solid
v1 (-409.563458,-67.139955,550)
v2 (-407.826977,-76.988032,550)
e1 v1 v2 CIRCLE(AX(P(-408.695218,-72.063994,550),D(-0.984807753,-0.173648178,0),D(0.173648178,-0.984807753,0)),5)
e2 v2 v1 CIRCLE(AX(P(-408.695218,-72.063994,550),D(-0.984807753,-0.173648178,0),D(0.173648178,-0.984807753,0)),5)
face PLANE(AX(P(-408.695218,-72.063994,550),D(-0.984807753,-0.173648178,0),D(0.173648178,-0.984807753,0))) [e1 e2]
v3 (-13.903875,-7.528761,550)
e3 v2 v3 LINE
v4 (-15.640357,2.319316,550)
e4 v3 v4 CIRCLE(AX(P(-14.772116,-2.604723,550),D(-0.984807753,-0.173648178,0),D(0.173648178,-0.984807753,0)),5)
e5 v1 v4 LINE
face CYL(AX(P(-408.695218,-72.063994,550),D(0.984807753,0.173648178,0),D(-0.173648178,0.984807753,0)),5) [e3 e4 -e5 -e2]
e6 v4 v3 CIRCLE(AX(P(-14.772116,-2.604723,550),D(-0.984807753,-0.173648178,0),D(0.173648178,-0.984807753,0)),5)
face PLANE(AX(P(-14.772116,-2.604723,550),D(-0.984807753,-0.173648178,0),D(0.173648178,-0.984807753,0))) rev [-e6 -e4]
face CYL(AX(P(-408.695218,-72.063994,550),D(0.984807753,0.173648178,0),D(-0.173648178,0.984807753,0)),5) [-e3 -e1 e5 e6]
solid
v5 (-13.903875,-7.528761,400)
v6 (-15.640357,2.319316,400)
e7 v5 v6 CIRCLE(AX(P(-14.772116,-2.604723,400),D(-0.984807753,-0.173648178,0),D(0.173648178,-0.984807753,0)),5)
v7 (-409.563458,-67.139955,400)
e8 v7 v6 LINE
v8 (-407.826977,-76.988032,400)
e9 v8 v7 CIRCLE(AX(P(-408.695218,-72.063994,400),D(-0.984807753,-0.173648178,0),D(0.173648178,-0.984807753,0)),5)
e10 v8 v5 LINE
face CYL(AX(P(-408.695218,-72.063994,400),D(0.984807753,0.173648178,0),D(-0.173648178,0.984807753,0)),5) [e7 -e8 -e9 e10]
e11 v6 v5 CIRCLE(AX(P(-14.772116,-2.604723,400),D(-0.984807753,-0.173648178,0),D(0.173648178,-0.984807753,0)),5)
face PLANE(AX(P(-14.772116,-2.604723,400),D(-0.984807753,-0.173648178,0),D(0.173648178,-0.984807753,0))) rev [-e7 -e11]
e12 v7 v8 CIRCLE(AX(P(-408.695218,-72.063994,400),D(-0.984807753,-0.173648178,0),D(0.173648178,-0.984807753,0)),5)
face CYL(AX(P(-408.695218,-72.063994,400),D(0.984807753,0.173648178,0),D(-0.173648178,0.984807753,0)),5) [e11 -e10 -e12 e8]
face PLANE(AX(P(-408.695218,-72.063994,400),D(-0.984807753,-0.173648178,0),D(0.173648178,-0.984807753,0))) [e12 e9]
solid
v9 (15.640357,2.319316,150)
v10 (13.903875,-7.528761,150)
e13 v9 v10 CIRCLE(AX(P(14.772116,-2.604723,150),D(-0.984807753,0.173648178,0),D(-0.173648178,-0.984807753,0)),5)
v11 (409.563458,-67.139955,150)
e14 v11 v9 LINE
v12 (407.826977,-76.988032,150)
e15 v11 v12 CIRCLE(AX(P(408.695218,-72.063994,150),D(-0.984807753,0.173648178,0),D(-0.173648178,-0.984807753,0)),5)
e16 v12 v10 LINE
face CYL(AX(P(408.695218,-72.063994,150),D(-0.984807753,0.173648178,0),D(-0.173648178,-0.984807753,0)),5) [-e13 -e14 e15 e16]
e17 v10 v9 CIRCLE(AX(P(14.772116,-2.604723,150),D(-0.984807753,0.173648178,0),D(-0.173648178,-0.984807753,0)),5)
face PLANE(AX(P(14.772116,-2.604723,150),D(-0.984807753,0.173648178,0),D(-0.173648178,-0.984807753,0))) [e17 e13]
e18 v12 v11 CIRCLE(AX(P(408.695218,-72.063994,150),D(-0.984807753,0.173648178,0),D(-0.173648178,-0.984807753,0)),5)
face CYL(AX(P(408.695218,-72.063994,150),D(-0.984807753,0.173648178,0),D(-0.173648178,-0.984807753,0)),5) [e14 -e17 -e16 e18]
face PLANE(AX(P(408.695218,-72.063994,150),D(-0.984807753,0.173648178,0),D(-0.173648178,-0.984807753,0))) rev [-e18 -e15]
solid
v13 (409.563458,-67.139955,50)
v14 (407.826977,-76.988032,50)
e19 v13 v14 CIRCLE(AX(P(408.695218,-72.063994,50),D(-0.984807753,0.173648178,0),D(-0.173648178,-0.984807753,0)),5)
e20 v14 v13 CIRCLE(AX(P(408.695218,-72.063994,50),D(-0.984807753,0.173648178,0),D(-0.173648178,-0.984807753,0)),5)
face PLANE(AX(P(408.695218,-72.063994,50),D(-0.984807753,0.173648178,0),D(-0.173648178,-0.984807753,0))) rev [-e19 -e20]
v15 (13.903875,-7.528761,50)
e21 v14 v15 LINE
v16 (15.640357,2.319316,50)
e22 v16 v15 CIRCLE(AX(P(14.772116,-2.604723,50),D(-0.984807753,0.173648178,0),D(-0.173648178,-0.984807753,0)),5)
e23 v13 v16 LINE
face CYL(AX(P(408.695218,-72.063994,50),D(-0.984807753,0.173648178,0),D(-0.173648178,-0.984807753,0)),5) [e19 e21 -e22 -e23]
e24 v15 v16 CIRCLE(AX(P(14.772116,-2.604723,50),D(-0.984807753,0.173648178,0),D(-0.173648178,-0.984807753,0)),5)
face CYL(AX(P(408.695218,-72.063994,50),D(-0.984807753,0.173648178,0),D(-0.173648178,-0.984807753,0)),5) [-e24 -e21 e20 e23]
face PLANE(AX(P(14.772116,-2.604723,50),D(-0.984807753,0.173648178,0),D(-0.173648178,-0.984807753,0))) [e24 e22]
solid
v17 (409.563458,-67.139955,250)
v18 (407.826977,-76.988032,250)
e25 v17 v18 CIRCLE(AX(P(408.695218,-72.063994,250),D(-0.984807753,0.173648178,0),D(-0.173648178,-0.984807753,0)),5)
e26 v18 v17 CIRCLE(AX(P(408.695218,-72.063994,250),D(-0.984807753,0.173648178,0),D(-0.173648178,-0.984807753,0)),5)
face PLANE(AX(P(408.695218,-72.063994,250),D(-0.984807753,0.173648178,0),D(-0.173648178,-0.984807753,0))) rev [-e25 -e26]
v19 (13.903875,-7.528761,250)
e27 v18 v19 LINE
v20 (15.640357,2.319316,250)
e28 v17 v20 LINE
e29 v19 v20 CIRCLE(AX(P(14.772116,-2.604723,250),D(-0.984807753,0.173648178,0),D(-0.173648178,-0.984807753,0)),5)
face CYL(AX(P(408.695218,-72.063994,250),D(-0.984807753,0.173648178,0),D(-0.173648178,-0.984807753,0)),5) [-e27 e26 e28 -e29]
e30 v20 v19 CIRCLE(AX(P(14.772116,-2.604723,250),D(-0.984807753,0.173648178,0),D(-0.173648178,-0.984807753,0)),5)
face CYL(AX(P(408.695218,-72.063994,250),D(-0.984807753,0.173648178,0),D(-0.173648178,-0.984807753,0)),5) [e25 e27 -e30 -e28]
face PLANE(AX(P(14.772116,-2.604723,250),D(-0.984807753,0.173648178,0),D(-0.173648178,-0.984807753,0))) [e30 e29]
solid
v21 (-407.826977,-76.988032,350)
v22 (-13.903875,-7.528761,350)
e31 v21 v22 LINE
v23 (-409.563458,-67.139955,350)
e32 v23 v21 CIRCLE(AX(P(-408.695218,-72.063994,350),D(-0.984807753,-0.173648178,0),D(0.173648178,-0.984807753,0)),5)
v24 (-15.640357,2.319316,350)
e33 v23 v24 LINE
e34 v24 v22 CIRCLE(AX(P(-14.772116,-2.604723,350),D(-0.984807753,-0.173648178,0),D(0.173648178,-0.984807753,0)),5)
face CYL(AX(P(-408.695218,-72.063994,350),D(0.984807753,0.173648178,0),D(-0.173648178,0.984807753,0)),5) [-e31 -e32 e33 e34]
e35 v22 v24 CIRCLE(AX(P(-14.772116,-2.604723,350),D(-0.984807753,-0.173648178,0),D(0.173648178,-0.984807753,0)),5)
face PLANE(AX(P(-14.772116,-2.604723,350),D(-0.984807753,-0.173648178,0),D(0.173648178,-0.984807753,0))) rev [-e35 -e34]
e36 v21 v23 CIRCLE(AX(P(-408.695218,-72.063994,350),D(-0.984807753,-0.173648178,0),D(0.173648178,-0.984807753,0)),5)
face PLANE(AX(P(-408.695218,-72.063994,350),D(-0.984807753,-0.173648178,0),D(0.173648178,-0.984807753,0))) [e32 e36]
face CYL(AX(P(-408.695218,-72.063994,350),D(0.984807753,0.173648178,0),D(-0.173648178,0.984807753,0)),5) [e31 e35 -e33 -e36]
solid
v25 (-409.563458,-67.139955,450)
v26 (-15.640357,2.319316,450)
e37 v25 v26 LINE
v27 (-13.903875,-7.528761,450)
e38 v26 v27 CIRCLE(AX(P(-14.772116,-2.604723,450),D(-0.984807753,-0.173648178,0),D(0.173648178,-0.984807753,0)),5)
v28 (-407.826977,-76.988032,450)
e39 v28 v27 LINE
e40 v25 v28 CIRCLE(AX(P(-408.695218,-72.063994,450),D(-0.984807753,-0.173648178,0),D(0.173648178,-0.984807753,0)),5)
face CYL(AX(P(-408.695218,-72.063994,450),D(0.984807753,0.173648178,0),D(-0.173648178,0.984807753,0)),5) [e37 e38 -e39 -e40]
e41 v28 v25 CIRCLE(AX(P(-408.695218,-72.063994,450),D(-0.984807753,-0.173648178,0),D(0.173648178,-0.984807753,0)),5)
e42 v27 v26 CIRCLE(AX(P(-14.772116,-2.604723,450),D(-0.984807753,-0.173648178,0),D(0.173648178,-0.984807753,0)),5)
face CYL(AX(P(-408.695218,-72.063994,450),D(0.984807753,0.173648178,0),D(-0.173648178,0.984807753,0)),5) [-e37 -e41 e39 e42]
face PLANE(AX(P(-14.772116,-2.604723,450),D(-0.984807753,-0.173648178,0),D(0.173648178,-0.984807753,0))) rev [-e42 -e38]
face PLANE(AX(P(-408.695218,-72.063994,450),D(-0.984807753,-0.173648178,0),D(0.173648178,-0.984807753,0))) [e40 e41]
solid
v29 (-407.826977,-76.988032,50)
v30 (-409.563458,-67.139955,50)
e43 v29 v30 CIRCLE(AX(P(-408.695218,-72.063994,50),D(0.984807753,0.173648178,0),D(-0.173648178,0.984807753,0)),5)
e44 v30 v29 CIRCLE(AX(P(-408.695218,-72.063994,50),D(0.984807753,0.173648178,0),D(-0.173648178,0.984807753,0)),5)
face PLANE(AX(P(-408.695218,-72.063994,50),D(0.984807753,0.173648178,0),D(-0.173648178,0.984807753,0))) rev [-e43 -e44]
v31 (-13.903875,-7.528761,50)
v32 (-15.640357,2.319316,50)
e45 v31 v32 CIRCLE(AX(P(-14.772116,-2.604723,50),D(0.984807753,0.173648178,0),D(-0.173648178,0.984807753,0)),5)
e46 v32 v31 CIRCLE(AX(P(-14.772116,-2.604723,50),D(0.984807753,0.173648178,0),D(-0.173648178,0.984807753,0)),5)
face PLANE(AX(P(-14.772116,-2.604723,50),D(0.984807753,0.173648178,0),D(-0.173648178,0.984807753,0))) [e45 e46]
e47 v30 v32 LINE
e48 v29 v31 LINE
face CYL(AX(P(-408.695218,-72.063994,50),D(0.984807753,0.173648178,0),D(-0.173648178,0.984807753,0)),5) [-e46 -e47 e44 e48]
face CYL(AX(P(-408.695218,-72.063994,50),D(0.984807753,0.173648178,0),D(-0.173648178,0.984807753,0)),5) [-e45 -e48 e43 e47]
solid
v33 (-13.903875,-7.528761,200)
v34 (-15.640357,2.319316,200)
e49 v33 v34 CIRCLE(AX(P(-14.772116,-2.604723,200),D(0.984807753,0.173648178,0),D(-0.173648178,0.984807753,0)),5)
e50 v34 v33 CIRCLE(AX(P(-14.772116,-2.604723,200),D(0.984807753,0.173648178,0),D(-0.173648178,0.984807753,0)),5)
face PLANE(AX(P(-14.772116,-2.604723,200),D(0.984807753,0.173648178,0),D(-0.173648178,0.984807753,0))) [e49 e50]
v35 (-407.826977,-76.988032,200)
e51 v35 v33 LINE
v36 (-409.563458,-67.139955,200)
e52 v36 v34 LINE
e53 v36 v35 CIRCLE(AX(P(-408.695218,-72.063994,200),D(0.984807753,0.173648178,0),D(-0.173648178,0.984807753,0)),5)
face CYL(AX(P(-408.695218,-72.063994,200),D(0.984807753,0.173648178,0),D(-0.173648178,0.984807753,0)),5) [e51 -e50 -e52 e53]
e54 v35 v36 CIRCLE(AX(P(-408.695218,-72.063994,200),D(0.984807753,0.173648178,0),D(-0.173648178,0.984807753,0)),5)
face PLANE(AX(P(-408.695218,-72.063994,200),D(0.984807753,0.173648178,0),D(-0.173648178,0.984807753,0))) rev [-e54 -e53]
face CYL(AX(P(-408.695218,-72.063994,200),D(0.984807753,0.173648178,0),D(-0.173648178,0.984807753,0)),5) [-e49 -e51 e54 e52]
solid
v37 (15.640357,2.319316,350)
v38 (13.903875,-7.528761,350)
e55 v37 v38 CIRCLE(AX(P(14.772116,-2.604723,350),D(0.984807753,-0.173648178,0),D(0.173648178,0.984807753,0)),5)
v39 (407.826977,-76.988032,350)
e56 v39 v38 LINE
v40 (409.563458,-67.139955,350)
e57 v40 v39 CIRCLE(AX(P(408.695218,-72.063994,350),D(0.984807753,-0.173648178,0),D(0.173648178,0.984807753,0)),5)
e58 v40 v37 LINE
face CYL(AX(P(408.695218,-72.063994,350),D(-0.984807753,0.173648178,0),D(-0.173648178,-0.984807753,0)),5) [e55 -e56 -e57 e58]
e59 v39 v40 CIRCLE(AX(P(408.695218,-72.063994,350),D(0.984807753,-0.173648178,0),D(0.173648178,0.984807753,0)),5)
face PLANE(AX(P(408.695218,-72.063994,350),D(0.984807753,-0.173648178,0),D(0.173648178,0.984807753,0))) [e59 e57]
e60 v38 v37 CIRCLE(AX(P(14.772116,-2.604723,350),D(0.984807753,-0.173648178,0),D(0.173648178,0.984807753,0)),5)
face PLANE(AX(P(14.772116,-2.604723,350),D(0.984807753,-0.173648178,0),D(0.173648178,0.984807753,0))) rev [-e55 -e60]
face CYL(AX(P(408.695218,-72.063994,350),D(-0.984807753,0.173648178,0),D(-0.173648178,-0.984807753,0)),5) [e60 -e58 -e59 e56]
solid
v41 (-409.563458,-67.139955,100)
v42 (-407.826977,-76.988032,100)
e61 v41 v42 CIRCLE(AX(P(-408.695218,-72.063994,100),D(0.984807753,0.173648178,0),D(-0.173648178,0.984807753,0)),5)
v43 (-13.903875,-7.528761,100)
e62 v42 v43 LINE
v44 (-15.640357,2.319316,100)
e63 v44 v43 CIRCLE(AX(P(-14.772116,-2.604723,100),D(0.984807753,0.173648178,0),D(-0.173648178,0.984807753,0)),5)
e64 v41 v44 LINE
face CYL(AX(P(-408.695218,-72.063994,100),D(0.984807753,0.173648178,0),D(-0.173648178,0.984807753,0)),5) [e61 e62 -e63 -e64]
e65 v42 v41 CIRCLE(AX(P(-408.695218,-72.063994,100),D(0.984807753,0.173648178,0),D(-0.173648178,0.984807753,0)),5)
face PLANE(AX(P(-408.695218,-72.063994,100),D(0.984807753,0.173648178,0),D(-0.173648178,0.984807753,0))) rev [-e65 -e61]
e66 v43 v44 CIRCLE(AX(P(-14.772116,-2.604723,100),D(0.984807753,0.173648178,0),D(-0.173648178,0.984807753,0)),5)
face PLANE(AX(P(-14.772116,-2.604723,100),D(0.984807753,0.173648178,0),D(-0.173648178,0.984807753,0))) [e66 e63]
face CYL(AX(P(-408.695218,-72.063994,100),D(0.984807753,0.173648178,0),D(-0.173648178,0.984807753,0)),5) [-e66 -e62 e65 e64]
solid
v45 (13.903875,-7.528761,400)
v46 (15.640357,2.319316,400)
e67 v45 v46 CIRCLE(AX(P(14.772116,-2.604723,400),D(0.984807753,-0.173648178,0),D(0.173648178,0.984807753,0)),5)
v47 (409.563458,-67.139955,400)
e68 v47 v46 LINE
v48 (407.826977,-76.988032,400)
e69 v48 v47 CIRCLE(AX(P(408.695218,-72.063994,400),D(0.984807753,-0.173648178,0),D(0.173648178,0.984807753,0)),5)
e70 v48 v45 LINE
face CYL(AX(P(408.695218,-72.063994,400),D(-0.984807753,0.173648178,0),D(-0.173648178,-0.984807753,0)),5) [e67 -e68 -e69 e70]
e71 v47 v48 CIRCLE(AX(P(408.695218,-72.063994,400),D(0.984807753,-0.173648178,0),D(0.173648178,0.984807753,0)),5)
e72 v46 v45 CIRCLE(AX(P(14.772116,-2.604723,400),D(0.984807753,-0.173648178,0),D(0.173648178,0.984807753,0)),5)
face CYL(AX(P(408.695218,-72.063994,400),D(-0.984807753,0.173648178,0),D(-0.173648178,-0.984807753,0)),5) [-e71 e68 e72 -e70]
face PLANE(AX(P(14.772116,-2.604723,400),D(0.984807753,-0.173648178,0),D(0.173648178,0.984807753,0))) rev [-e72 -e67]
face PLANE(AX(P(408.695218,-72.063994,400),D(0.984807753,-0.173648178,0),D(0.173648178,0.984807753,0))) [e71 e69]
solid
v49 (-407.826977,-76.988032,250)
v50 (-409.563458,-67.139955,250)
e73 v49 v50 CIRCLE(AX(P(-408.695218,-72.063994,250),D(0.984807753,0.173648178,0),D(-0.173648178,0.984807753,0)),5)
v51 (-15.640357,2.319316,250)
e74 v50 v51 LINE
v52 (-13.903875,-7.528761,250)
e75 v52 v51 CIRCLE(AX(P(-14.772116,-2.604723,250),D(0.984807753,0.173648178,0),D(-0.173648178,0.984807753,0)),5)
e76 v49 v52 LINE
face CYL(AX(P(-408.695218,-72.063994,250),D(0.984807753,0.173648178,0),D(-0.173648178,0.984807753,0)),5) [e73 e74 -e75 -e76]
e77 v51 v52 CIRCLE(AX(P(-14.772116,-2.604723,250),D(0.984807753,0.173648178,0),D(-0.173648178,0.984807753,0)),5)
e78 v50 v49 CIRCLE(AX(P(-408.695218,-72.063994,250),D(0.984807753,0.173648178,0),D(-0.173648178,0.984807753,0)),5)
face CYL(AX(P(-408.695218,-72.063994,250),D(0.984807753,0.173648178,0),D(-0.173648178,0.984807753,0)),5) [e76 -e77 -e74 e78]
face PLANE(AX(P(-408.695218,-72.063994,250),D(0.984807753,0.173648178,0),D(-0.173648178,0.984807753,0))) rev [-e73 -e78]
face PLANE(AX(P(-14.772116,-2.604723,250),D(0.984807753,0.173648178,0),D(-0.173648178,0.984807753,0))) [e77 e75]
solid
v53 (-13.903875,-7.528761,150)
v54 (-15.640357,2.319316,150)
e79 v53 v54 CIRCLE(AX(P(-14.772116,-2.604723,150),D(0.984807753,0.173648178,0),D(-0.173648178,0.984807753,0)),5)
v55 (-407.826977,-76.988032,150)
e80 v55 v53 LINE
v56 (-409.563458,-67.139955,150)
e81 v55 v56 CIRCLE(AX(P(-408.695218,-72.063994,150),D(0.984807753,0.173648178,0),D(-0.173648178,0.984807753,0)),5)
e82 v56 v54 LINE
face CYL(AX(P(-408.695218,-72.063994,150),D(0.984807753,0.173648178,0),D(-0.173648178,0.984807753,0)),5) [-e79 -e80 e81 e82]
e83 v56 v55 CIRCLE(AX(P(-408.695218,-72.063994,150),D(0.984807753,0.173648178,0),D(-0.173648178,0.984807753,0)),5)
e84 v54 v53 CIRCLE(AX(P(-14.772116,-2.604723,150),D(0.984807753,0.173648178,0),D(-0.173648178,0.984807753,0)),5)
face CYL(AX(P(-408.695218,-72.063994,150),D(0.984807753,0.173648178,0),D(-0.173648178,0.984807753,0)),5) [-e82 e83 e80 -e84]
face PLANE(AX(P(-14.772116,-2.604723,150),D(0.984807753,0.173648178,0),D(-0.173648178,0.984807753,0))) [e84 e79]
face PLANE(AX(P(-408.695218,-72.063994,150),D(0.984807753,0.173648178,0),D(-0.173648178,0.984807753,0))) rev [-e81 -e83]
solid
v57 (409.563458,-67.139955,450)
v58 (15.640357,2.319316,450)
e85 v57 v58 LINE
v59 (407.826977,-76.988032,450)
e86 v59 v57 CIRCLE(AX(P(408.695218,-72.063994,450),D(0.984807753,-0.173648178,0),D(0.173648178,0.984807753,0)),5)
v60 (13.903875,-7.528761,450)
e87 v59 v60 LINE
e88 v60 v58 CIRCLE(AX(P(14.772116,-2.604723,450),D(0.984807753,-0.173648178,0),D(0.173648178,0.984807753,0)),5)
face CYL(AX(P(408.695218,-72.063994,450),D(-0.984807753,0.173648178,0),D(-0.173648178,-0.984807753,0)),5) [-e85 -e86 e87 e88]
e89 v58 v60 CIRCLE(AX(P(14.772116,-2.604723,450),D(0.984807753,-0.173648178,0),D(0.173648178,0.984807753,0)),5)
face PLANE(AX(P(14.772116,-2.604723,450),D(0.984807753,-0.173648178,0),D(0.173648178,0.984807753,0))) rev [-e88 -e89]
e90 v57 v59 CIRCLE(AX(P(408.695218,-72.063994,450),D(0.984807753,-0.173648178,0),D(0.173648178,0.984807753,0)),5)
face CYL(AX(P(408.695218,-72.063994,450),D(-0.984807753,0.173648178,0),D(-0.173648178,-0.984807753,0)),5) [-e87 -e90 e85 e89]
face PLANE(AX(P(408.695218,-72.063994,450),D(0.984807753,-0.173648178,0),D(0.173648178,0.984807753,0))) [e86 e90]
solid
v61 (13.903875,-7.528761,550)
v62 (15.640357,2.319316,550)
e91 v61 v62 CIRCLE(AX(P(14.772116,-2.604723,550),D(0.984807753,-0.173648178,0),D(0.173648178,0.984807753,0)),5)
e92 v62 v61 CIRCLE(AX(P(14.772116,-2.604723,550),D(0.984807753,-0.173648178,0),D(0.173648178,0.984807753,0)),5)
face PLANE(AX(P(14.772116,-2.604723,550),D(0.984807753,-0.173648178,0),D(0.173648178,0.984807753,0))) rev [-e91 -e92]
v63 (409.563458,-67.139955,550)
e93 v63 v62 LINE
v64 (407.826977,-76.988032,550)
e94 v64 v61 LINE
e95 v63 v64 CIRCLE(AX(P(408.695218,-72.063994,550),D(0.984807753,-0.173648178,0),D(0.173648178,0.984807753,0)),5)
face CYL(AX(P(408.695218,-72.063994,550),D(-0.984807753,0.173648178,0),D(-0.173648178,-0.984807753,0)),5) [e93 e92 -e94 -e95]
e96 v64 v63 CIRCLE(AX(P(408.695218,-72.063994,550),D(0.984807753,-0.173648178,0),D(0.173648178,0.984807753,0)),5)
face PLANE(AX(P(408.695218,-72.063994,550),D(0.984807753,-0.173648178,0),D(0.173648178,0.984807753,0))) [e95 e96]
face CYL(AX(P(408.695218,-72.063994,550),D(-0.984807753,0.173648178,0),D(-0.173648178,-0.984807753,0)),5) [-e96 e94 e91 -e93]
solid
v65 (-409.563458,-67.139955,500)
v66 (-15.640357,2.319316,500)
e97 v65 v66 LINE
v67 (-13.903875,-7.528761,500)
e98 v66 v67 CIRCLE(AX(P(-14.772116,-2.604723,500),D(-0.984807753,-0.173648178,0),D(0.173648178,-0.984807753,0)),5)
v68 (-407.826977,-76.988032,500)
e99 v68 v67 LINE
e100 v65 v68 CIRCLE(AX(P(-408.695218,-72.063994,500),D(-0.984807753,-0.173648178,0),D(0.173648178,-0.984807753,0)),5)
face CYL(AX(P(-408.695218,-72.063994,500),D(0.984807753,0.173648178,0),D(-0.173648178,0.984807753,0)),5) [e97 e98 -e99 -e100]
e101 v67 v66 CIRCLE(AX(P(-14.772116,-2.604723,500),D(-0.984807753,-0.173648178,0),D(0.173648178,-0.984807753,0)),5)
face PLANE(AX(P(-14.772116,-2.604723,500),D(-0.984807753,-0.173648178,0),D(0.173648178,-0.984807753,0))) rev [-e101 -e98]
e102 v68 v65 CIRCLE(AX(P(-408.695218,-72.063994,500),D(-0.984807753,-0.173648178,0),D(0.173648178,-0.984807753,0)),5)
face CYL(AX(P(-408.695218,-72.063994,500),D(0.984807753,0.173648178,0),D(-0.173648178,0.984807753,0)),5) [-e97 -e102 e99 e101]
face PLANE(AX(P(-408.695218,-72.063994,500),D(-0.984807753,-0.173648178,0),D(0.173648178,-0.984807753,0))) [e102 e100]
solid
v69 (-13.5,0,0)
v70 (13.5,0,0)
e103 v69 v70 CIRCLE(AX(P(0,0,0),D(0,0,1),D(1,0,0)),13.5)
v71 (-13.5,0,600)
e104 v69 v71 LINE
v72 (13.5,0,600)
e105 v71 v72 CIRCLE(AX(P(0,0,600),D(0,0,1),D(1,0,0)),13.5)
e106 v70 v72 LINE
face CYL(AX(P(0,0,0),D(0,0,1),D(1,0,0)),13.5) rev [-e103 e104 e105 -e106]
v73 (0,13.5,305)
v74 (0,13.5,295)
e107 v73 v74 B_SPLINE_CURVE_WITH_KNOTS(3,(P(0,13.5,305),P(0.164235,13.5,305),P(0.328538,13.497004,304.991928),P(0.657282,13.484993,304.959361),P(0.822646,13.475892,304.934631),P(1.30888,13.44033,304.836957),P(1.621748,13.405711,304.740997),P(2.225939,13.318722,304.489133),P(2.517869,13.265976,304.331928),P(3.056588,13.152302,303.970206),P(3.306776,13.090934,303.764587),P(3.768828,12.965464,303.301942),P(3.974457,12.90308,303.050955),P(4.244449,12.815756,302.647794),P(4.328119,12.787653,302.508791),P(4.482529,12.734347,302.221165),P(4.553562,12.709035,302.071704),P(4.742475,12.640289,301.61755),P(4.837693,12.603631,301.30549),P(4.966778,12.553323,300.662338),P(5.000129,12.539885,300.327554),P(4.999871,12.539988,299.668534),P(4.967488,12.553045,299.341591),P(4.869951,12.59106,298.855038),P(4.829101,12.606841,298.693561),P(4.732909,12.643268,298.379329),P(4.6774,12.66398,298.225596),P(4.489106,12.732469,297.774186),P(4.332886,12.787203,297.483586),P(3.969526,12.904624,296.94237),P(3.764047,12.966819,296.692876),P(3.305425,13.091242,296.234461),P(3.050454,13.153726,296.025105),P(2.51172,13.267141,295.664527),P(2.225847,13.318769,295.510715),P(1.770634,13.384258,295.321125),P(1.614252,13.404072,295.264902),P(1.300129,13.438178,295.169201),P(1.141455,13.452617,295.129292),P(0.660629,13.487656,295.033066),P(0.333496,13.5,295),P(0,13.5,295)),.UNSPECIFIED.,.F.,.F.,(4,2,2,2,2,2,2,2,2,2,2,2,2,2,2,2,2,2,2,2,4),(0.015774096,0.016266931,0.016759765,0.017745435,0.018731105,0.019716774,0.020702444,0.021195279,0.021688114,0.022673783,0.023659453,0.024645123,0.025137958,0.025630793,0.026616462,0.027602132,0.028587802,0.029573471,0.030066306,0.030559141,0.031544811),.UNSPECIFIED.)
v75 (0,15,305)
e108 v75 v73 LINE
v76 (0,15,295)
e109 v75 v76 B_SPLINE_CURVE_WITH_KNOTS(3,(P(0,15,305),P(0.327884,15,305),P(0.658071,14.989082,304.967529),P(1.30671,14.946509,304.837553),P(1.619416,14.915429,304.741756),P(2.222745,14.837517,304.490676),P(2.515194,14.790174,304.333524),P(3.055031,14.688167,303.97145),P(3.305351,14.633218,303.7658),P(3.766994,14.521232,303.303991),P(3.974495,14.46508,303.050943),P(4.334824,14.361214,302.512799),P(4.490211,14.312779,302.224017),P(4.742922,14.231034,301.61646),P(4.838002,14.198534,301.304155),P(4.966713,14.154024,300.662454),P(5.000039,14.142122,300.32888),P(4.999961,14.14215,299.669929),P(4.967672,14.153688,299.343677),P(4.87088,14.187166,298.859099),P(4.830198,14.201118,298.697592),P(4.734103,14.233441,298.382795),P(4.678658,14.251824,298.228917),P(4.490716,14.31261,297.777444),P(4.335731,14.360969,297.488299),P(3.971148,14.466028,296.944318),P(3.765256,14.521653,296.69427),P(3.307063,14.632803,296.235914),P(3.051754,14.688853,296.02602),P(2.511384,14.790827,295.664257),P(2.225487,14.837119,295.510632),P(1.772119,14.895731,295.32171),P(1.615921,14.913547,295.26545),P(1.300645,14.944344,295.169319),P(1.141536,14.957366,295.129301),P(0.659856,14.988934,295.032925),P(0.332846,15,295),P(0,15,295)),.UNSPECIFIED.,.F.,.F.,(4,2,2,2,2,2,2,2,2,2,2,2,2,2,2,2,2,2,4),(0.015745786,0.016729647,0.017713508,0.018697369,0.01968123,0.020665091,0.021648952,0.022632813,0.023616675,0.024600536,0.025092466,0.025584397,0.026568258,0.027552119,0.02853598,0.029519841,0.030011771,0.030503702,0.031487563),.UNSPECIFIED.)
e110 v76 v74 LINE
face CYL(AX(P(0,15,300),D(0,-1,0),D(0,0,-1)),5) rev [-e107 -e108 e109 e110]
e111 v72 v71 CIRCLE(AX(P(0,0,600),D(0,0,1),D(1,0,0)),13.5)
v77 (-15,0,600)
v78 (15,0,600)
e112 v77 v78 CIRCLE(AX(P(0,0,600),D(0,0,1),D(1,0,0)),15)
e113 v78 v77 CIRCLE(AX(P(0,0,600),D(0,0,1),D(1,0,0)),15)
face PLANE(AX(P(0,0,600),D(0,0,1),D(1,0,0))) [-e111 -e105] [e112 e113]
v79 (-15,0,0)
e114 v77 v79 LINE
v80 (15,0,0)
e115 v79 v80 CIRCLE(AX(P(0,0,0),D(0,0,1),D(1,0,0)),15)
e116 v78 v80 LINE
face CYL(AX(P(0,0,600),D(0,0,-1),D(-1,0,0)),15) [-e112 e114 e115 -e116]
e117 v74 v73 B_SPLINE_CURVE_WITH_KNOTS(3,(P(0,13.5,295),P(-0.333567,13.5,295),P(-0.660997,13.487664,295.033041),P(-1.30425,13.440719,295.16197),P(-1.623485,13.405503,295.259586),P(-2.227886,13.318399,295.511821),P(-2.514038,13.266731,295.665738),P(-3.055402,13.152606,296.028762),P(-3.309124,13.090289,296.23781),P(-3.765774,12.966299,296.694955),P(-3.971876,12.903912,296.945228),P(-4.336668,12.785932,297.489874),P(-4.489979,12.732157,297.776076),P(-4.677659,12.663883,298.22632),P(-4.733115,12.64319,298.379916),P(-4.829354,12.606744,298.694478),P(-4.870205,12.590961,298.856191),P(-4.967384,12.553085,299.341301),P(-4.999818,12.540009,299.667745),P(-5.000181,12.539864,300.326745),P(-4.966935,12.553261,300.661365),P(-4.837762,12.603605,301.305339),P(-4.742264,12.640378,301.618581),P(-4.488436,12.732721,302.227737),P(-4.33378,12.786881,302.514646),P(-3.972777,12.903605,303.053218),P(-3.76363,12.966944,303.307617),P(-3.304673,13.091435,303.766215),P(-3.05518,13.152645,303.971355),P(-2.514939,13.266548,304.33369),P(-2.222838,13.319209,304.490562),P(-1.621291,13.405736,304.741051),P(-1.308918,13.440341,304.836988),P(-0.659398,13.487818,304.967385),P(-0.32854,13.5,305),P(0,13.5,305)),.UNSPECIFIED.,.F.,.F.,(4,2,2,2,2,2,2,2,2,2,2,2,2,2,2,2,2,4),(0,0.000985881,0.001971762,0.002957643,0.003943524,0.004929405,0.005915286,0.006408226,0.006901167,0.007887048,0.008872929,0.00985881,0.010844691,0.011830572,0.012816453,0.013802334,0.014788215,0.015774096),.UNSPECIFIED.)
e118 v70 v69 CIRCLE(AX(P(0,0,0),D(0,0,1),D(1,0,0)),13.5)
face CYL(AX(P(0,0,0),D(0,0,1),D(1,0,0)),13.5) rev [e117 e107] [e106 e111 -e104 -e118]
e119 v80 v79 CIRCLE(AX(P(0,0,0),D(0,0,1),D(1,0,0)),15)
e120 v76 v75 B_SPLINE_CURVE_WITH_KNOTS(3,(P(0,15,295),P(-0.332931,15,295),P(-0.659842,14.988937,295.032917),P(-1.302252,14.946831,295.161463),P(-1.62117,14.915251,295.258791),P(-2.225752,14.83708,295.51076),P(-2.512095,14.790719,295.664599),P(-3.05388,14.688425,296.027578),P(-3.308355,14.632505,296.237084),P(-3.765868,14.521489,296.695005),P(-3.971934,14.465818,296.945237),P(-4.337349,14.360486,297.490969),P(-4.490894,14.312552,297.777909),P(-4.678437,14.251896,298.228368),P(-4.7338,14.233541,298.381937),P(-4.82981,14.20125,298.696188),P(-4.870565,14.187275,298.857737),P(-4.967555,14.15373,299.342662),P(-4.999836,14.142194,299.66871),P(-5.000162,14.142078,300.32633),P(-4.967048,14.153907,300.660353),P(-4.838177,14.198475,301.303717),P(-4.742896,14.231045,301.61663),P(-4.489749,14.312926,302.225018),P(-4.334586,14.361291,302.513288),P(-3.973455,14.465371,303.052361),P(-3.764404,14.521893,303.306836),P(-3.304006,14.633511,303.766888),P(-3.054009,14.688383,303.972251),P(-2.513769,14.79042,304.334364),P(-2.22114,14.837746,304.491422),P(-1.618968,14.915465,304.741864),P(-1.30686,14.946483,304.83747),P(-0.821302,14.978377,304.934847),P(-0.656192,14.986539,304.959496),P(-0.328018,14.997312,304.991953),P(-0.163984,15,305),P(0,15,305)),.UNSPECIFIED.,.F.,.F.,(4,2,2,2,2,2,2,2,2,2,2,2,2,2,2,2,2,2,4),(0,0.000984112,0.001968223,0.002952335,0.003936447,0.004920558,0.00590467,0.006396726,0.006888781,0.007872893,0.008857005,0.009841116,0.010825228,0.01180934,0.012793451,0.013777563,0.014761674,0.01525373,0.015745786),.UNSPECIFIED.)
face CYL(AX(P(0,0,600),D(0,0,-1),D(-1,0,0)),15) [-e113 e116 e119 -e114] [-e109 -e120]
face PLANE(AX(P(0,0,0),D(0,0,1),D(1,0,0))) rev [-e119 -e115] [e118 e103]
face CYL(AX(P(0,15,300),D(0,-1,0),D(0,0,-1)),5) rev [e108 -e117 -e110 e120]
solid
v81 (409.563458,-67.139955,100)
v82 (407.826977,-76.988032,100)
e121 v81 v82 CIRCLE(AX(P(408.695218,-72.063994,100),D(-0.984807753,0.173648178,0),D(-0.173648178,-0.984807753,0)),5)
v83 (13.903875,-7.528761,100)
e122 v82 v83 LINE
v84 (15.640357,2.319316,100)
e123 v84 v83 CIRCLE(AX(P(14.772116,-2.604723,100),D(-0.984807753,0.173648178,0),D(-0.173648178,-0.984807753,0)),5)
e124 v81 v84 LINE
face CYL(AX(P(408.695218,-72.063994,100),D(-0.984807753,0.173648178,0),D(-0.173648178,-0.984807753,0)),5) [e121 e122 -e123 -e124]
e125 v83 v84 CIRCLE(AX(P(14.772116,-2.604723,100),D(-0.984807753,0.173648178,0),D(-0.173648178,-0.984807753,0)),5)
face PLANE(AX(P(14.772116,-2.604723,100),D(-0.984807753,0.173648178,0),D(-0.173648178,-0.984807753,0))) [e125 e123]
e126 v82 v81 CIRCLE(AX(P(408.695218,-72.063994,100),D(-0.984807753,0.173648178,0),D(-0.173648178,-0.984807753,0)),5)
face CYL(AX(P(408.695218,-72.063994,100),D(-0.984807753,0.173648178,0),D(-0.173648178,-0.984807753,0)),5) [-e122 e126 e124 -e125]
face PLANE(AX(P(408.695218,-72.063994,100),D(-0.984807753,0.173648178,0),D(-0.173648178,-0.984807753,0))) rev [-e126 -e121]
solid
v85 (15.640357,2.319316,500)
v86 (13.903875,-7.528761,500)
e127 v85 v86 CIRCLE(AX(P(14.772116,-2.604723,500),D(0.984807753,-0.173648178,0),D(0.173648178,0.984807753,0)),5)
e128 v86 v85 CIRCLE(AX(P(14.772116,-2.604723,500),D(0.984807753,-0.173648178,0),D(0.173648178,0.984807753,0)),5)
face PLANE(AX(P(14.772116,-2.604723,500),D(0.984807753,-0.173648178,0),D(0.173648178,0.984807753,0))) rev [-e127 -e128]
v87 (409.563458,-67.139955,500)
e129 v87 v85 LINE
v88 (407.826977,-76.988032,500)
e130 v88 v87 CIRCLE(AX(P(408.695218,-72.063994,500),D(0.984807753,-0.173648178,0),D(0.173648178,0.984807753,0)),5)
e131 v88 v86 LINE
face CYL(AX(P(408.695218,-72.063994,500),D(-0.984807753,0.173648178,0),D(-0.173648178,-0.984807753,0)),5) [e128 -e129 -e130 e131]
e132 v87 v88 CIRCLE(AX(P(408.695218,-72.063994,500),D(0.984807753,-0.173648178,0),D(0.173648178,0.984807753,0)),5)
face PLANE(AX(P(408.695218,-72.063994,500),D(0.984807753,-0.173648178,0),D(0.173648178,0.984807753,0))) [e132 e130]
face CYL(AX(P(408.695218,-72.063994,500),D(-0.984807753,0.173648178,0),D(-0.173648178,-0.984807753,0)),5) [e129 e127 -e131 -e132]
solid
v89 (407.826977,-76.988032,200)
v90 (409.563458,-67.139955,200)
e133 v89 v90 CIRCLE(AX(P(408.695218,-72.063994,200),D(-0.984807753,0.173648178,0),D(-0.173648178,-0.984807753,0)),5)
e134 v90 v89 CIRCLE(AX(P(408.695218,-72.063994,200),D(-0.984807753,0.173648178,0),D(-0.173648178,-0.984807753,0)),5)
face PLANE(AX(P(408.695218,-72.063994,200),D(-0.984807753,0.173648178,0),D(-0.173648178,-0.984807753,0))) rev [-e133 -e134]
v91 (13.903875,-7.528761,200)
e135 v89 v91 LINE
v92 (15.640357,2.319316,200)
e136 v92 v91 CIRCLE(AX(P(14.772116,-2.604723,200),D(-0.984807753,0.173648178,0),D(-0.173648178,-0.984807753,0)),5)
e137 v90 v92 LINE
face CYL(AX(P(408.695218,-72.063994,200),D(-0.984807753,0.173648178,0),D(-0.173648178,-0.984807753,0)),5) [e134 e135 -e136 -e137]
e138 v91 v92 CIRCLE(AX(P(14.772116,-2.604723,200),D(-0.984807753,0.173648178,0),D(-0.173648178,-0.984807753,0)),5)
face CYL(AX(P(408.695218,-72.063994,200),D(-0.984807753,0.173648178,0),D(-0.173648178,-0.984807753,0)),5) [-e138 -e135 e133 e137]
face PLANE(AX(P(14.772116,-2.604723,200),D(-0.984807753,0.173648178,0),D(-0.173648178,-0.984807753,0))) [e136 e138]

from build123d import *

# Parameters (mm, degrees)
SKETCH1_R              = 15
BOSS_EXTRUDE1_DEPTH    = 600
SKETCH5_R              = 5
BOSS_EXTRUDE3_DEPTH    = 400
BOSS_EXTRUDE3_2_DEPTH  = 400
BOSS_EXTRUDE3_3_DEPTH  = 400
BOSS_EXTRUDE3_4_DEPTH  = 400
BOSS_EXTRUDE3_5_DEPTH  = 400
BOSS_EXTRUDE3_6_DEPTH  = 400
BOSS_EXTRUDE3_7_DEPTH  = 400
BOSS_EXTRUDE3_8_DEPTH  = 400
BOSS_EXTRUDE3_9_DEPTH  = 400
BOSS_EXTRUDE3_10_DEPTH = 400
SKETCH6_R              = 5
BOSS_EXTRUDE4_DEPTH    = 400
BOSS_EXTRUDE4_2_DEPTH  = 400
BOSS_EXTRUDE4_3_DEPTH  = 400
BOSS_EXTRUDE4_4_DEPTH  = 400
BOSS_EXTRUDE4_5_DEPTH  = 400
BOSS_EXTRUDE4_6_DEPTH  = 400
BOSS_EXTRUDE4_7_DEPTH  = 400
BOSS_EXTRUDE4_8_DEPTH  = 400
BOSS_EXTRUDE4_9_DEPTH  = 400
BOSS_EXTRUDE4_10_DEPTH = 400
SKETCH7_R              = 5
CUT_EXTRUDE1_DEPTH     = 731.526784995
SKETCH8_R              = 13.5
CUT_EXTRUDE2_DEPTH     = 731.526785077


with BuildPart() as part:
    # Sketch1 → Boss-Extrude1 (new body)
    with BuildSketch(Plane.XY):
        Circle(SKETCH1_R)
    extrude(amount=BOSS_EXTRUDE1_DEPTH)

    # Sketch7 → Cut-Extrude1 (cut, through all)
    with BuildSketch(Plane(origin=(0, 0, 0), x_dir=(1, 0, 0), z_dir=(0, 1, 0))):
        with Locations(Location((0, -300, 0), (0, 0, 90))):
            Circle(SKETCH7_R)
    extrude(amount=CUT_EXTRUDE1_DEPTH, mode=Mode.SUBTRACT)

    # Sketch8 → Cut-Extrude2 (cut, through all)
    with BuildSketch(Plane.XY.offset(600)):
        Circle(SKETCH8_R)
    extrude(amount=-CUT_EXTRUDE2_DEPTH, mode=Mode.SUBTRACT)


with BuildPart() as body_2:
    # Sketch5 → Boss-Extrude3 (new body)
    with BuildSketch(Plane(origin=(-14.772116295, -2.604722665, 0), x_dir=(0, 0, -1), z_dir=(-0.9848077530122086, -0.17364817766692736, 0))):
        with Locations(Location((-350, 0, 0), (0, 0, 90))):
            Circle(SKETCH5_R)
    extrude(amount=BOSS_EXTRUDE3_DEPTH)


with BuildPart() as body_3:
    # Sketch5 → Boss-Extrude3 2 (new body)
    with BuildSketch(Plane(origin=(-14.772116295, -2.604722665, 0), x_dir=(0, 0, -1), z_dir=(-0.9848077530122086, -0.17364817766692736, 0))):
        with Locations(Location((-400, 0, 0), (0, 0, 90))):
            Circle(SKETCH5_R)
    extrude(amount=BOSS_EXTRUDE3_2_DEPTH)


with BuildPart() as body_4:
    # Sketch5 → Boss-Extrude3 3 (new body)
    with BuildSketch(Plane(origin=(-14.772116295, -2.604722665, 0), x_dir=(0, 0, -1), z_dir=(-0.9848077530122086, -0.17364817766692736, 0))):
        with Locations(Location((-450, 0, 0), (0, 0, 90))):
            Circle(SKETCH5_R)
    extrude(amount=BOSS_EXTRUDE3_3_DEPTH)


with BuildPart() as body_5:
    # Sketch5 → Boss-Extrude3 4 (new body)
    with BuildSketch(Plane(origin=(-14.772116295, -2.604722665, 0), x_dir=(0, 0, -1), z_dir=(-0.9848077530122086, -0.17364817766692736, 0))):
        with Locations(Location((-500, 0, 0), (0, 0, 90))):
            Circle(SKETCH5_R)
    extrude(amount=BOSS_EXTRUDE3_4_DEPTH)


with BuildPart() as body_6:
    # Sketch5 → Boss-Extrude3 5 (new body)
    with BuildSketch(Plane(origin=(-14.772116295, -2.604722665, 0), x_dir=(0, 0, -1), z_dir=(-0.9848077530122086, -0.17364817766692736, 0))):
        with Locations(Location((-550, 0, 0), (0, 0, 90))):
            Circle(SKETCH5_R)
    extrude(amount=BOSS_EXTRUDE3_5_DEPTH)


with BuildPart() as body_7:
    # Sketch5 → Boss-Extrude3 6 (new body)
    with BuildSketch(Plane(origin=(-14.772116295, -2.604722665, 0), x_dir=(0, 0, -1), z_dir=(-0.9848077530122086, -0.17364817766692736, 0))):
        with Locations(Location((-250, 0, 0), (0, 0, 270))):
            Circle(SKETCH5_R)
    extrude(amount=BOSS_EXTRUDE3_6_DEPTH)


with BuildPart() as body_8:
    # Sketch5 → Boss-Extrude3 7 (new body)
    with BuildSketch(Plane(origin=(-14.772116295, -2.604722665, 0), x_dir=(0, 0, -1), z_dir=(-0.9848077530122086, -0.17364817766692736, 0))):
        with Locations(Location((-200, 0, 0), (0, 0, 270))):
            Circle(SKETCH5_R)
    extrude(amount=BOSS_EXTRUDE3_7_DEPTH)


with BuildPart() as body_9:
    # Sketch5 → Boss-Extrude3 8 (new body)
    with BuildSketch(Plane(origin=(-14.772116295, -2.604722665, 0), x_dir=(0, 0, -1), z_dir=(-0.9848077530122086, -0.17364817766692736, 0))):
        with Locations(Location((-150, 0, 0), (0, 0, 270))):
            Circle(SKETCH5_R)
    extrude(amount=BOSS_EXTRUDE3_8_DEPTH)


with BuildPart() as body_10:
    # Sketch5 → Boss-Extrude3 9 (new body)
    with BuildSketch(Plane(origin=(-14.772116295, -2.604722665, 0), x_dir=(0, 0, -1), z_dir=(-0.9848077530122086, -0.17364817766692736, 0))):
        with Locations(Location((-100, 0, 0), (0, 0, 270))):
            Circle(SKETCH5_R)
    extrude(amount=BOSS_EXTRUDE3_9_DEPTH)


with BuildPart() as body_11:
    # Sketch5 → Boss-Extrude3 10 (new body)
    with BuildSketch(Plane(origin=(-14.772116295, -2.604722665, 0), x_dir=(0, 0, -1), z_dir=(-0.9848077530122086, -0.17364817766692736, 0))):
        with Locations(Location((-50, 0, 0), (0, 0, 270))):
            Circle(SKETCH5_R)
    extrude(amount=BOSS_EXTRUDE3_10_DEPTH)


with BuildPart() as body_12:
    # Sketch6 → Boss-Extrude4 (new body)
    with BuildSketch(Plane(origin=(14.772116295, -2.604722665, 0), x_dir=(0, 0, -1), z_dir=(0.9848077530122075, -0.17364817766693402, 0))):
        with Locations(Location((-550, 0, 0), (0, 0, 90))):
            Circle(SKETCH6_R)
    extrude(amount=BOSS_EXTRUDE4_DEPTH)


with BuildPart() as body_13:
    # Sketch6 → Boss-Extrude4 2 (new body)
    with BuildSketch(Plane(origin=(14.772116295, -2.604722665, 0), x_dir=(0, 0, -1), z_dir=(0.9848077530122075, -0.17364817766693402, 0))):
        with Locations(Location((-500, 0, 0), (0, 0, 90))):
            Circle(SKETCH6_R)
    extrude(amount=BOSS_EXTRUDE4_2_DEPTH)


with BuildPart() as body_14:
    # Sketch6 → Boss-Extrude4 3 (new body)
    with BuildSketch(Plane(origin=(14.772116295, -2.604722665, 0), x_dir=(0, 0, -1), z_dir=(0.9848077530122075, -0.17364817766693402, 0))):
        with Locations(Location((-450, 0, 0), (0, 0, 90))):
            Circle(SKETCH6_R)
    extrude(amount=BOSS_EXTRUDE4_3_DEPTH)


with BuildPart() as body_15:
    # Sketch6 → Boss-Extrude4 4 (new body)
    with BuildSketch(Plane(origin=(14.772116295, -2.604722665, 0), x_dir=(0, 0, -1), z_dir=(0.9848077530122075, -0.17364817766693402, 0))):
        with Locations(Location((-400, 0, 0), (0, 0, 90))):
            Circle(SKETCH6_R)
    extrude(amount=BOSS_EXTRUDE4_4_DEPTH)


with BuildPart() as body_16:
    # Sketch6 → Boss-Extrude4 5 (new body)
    with BuildSketch(Plane(origin=(14.772116295, -2.604722665, 0), x_dir=(0, 0, -1), z_dir=(0.9848077530122075, -0.17364817766693402, 0))):
        with Locations(Location((-350, 0, 0), (0, 0, 90))):
            Circle(SKETCH6_R)
    extrude(amount=BOSS_EXTRUDE4_5_DEPTH)


with BuildPart() as body_17:
    # Sketch6 → Boss-Extrude4 6 (new body)
    with BuildSketch(Plane(origin=(14.772116295, -2.604722665, 0), x_dir=(0, 0, -1), z_dir=(0.9848077530122075, -0.17364817766693402, 0))):
        with Locations(Location((-250, 0, 0), (0, 0, 270))):
            Circle(SKETCH6_R)
    extrude(amount=BOSS_EXTRUDE4_6_DEPTH)


with BuildPart() as body_18:
    # Sketch6 → Boss-Extrude4 7 (new body)
    with BuildSketch(Plane(origin=(14.772116295, -2.604722665, 0), x_dir=(0, 0, -1), z_dir=(0.9848077530122075, -0.17364817766693402, 0))):
        with Locations(Location((-200, 0, 0), (0, 0, 270))):
            Circle(SKETCH6_R)
    extrude(amount=BOSS_EXTRUDE4_7_DEPTH)


with BuildPart() as body_19:
    # Sketch6 → Boss-Extrude4 8 (new body)
    with BuildSketch(Plane(origin=(14.772116295, -2.604722665, 0), x_dir=(0, 0, -1), z_dir=(0.9848077530122075, -0.17364817766693402, 0))):
        with Locations(Location((-150, 0, 0), (0, 0, 270))):
            Circle(SKETCH6_R)
    extrude(amount=BOSS_EXTRUDE4_8_DEPTH)


with BuildPart() as body_20:
    # Sketch6 → Boss-Extrude4 9 (new body)
    with BuildSketch(Plane(origin=(14.772116295, -2.604722665, 0), x_dir=(0, 0, -1), z_dir=(0.9848077530122075, -0.17364817766693402, 0))):
        with Locations(Location((-100, 0, 0), (0, 0, 270))):
            Circle(SKETCH6_R)
    extrude(amount=BOSS_EXTRUDE4_9_DEPTH)


with BuildPart() as body_21:
    # Sketch6 → Boss-Extrude4 10 (new body)
    with BuildSketch(Plane(origin=(14.772116295, -2.604722665, 0), x_dir=(0, 0, -1), z_dir=(0.9848077530122075, -0.17364817766693402, 0))):
        with Locations(Location((-50, 0, 0), (0, 0, 270))):
            Circle(SKETCH6_R)
    extrude(amount=BOSS_EXTRUDE4_10_DEPTH)


solid = Compound([part.part, body_2.part, body_3.part, body_4.part, body_5.part, body_6.part, body_7.part, body_8.part, body_9.part, body_10.part, body_11.part, body_12.part, body_13.part, body_14.part, body_15.part, body_16.part, body_17.part, body_18.part, body_19.part, body_20.part, body_21.part])
